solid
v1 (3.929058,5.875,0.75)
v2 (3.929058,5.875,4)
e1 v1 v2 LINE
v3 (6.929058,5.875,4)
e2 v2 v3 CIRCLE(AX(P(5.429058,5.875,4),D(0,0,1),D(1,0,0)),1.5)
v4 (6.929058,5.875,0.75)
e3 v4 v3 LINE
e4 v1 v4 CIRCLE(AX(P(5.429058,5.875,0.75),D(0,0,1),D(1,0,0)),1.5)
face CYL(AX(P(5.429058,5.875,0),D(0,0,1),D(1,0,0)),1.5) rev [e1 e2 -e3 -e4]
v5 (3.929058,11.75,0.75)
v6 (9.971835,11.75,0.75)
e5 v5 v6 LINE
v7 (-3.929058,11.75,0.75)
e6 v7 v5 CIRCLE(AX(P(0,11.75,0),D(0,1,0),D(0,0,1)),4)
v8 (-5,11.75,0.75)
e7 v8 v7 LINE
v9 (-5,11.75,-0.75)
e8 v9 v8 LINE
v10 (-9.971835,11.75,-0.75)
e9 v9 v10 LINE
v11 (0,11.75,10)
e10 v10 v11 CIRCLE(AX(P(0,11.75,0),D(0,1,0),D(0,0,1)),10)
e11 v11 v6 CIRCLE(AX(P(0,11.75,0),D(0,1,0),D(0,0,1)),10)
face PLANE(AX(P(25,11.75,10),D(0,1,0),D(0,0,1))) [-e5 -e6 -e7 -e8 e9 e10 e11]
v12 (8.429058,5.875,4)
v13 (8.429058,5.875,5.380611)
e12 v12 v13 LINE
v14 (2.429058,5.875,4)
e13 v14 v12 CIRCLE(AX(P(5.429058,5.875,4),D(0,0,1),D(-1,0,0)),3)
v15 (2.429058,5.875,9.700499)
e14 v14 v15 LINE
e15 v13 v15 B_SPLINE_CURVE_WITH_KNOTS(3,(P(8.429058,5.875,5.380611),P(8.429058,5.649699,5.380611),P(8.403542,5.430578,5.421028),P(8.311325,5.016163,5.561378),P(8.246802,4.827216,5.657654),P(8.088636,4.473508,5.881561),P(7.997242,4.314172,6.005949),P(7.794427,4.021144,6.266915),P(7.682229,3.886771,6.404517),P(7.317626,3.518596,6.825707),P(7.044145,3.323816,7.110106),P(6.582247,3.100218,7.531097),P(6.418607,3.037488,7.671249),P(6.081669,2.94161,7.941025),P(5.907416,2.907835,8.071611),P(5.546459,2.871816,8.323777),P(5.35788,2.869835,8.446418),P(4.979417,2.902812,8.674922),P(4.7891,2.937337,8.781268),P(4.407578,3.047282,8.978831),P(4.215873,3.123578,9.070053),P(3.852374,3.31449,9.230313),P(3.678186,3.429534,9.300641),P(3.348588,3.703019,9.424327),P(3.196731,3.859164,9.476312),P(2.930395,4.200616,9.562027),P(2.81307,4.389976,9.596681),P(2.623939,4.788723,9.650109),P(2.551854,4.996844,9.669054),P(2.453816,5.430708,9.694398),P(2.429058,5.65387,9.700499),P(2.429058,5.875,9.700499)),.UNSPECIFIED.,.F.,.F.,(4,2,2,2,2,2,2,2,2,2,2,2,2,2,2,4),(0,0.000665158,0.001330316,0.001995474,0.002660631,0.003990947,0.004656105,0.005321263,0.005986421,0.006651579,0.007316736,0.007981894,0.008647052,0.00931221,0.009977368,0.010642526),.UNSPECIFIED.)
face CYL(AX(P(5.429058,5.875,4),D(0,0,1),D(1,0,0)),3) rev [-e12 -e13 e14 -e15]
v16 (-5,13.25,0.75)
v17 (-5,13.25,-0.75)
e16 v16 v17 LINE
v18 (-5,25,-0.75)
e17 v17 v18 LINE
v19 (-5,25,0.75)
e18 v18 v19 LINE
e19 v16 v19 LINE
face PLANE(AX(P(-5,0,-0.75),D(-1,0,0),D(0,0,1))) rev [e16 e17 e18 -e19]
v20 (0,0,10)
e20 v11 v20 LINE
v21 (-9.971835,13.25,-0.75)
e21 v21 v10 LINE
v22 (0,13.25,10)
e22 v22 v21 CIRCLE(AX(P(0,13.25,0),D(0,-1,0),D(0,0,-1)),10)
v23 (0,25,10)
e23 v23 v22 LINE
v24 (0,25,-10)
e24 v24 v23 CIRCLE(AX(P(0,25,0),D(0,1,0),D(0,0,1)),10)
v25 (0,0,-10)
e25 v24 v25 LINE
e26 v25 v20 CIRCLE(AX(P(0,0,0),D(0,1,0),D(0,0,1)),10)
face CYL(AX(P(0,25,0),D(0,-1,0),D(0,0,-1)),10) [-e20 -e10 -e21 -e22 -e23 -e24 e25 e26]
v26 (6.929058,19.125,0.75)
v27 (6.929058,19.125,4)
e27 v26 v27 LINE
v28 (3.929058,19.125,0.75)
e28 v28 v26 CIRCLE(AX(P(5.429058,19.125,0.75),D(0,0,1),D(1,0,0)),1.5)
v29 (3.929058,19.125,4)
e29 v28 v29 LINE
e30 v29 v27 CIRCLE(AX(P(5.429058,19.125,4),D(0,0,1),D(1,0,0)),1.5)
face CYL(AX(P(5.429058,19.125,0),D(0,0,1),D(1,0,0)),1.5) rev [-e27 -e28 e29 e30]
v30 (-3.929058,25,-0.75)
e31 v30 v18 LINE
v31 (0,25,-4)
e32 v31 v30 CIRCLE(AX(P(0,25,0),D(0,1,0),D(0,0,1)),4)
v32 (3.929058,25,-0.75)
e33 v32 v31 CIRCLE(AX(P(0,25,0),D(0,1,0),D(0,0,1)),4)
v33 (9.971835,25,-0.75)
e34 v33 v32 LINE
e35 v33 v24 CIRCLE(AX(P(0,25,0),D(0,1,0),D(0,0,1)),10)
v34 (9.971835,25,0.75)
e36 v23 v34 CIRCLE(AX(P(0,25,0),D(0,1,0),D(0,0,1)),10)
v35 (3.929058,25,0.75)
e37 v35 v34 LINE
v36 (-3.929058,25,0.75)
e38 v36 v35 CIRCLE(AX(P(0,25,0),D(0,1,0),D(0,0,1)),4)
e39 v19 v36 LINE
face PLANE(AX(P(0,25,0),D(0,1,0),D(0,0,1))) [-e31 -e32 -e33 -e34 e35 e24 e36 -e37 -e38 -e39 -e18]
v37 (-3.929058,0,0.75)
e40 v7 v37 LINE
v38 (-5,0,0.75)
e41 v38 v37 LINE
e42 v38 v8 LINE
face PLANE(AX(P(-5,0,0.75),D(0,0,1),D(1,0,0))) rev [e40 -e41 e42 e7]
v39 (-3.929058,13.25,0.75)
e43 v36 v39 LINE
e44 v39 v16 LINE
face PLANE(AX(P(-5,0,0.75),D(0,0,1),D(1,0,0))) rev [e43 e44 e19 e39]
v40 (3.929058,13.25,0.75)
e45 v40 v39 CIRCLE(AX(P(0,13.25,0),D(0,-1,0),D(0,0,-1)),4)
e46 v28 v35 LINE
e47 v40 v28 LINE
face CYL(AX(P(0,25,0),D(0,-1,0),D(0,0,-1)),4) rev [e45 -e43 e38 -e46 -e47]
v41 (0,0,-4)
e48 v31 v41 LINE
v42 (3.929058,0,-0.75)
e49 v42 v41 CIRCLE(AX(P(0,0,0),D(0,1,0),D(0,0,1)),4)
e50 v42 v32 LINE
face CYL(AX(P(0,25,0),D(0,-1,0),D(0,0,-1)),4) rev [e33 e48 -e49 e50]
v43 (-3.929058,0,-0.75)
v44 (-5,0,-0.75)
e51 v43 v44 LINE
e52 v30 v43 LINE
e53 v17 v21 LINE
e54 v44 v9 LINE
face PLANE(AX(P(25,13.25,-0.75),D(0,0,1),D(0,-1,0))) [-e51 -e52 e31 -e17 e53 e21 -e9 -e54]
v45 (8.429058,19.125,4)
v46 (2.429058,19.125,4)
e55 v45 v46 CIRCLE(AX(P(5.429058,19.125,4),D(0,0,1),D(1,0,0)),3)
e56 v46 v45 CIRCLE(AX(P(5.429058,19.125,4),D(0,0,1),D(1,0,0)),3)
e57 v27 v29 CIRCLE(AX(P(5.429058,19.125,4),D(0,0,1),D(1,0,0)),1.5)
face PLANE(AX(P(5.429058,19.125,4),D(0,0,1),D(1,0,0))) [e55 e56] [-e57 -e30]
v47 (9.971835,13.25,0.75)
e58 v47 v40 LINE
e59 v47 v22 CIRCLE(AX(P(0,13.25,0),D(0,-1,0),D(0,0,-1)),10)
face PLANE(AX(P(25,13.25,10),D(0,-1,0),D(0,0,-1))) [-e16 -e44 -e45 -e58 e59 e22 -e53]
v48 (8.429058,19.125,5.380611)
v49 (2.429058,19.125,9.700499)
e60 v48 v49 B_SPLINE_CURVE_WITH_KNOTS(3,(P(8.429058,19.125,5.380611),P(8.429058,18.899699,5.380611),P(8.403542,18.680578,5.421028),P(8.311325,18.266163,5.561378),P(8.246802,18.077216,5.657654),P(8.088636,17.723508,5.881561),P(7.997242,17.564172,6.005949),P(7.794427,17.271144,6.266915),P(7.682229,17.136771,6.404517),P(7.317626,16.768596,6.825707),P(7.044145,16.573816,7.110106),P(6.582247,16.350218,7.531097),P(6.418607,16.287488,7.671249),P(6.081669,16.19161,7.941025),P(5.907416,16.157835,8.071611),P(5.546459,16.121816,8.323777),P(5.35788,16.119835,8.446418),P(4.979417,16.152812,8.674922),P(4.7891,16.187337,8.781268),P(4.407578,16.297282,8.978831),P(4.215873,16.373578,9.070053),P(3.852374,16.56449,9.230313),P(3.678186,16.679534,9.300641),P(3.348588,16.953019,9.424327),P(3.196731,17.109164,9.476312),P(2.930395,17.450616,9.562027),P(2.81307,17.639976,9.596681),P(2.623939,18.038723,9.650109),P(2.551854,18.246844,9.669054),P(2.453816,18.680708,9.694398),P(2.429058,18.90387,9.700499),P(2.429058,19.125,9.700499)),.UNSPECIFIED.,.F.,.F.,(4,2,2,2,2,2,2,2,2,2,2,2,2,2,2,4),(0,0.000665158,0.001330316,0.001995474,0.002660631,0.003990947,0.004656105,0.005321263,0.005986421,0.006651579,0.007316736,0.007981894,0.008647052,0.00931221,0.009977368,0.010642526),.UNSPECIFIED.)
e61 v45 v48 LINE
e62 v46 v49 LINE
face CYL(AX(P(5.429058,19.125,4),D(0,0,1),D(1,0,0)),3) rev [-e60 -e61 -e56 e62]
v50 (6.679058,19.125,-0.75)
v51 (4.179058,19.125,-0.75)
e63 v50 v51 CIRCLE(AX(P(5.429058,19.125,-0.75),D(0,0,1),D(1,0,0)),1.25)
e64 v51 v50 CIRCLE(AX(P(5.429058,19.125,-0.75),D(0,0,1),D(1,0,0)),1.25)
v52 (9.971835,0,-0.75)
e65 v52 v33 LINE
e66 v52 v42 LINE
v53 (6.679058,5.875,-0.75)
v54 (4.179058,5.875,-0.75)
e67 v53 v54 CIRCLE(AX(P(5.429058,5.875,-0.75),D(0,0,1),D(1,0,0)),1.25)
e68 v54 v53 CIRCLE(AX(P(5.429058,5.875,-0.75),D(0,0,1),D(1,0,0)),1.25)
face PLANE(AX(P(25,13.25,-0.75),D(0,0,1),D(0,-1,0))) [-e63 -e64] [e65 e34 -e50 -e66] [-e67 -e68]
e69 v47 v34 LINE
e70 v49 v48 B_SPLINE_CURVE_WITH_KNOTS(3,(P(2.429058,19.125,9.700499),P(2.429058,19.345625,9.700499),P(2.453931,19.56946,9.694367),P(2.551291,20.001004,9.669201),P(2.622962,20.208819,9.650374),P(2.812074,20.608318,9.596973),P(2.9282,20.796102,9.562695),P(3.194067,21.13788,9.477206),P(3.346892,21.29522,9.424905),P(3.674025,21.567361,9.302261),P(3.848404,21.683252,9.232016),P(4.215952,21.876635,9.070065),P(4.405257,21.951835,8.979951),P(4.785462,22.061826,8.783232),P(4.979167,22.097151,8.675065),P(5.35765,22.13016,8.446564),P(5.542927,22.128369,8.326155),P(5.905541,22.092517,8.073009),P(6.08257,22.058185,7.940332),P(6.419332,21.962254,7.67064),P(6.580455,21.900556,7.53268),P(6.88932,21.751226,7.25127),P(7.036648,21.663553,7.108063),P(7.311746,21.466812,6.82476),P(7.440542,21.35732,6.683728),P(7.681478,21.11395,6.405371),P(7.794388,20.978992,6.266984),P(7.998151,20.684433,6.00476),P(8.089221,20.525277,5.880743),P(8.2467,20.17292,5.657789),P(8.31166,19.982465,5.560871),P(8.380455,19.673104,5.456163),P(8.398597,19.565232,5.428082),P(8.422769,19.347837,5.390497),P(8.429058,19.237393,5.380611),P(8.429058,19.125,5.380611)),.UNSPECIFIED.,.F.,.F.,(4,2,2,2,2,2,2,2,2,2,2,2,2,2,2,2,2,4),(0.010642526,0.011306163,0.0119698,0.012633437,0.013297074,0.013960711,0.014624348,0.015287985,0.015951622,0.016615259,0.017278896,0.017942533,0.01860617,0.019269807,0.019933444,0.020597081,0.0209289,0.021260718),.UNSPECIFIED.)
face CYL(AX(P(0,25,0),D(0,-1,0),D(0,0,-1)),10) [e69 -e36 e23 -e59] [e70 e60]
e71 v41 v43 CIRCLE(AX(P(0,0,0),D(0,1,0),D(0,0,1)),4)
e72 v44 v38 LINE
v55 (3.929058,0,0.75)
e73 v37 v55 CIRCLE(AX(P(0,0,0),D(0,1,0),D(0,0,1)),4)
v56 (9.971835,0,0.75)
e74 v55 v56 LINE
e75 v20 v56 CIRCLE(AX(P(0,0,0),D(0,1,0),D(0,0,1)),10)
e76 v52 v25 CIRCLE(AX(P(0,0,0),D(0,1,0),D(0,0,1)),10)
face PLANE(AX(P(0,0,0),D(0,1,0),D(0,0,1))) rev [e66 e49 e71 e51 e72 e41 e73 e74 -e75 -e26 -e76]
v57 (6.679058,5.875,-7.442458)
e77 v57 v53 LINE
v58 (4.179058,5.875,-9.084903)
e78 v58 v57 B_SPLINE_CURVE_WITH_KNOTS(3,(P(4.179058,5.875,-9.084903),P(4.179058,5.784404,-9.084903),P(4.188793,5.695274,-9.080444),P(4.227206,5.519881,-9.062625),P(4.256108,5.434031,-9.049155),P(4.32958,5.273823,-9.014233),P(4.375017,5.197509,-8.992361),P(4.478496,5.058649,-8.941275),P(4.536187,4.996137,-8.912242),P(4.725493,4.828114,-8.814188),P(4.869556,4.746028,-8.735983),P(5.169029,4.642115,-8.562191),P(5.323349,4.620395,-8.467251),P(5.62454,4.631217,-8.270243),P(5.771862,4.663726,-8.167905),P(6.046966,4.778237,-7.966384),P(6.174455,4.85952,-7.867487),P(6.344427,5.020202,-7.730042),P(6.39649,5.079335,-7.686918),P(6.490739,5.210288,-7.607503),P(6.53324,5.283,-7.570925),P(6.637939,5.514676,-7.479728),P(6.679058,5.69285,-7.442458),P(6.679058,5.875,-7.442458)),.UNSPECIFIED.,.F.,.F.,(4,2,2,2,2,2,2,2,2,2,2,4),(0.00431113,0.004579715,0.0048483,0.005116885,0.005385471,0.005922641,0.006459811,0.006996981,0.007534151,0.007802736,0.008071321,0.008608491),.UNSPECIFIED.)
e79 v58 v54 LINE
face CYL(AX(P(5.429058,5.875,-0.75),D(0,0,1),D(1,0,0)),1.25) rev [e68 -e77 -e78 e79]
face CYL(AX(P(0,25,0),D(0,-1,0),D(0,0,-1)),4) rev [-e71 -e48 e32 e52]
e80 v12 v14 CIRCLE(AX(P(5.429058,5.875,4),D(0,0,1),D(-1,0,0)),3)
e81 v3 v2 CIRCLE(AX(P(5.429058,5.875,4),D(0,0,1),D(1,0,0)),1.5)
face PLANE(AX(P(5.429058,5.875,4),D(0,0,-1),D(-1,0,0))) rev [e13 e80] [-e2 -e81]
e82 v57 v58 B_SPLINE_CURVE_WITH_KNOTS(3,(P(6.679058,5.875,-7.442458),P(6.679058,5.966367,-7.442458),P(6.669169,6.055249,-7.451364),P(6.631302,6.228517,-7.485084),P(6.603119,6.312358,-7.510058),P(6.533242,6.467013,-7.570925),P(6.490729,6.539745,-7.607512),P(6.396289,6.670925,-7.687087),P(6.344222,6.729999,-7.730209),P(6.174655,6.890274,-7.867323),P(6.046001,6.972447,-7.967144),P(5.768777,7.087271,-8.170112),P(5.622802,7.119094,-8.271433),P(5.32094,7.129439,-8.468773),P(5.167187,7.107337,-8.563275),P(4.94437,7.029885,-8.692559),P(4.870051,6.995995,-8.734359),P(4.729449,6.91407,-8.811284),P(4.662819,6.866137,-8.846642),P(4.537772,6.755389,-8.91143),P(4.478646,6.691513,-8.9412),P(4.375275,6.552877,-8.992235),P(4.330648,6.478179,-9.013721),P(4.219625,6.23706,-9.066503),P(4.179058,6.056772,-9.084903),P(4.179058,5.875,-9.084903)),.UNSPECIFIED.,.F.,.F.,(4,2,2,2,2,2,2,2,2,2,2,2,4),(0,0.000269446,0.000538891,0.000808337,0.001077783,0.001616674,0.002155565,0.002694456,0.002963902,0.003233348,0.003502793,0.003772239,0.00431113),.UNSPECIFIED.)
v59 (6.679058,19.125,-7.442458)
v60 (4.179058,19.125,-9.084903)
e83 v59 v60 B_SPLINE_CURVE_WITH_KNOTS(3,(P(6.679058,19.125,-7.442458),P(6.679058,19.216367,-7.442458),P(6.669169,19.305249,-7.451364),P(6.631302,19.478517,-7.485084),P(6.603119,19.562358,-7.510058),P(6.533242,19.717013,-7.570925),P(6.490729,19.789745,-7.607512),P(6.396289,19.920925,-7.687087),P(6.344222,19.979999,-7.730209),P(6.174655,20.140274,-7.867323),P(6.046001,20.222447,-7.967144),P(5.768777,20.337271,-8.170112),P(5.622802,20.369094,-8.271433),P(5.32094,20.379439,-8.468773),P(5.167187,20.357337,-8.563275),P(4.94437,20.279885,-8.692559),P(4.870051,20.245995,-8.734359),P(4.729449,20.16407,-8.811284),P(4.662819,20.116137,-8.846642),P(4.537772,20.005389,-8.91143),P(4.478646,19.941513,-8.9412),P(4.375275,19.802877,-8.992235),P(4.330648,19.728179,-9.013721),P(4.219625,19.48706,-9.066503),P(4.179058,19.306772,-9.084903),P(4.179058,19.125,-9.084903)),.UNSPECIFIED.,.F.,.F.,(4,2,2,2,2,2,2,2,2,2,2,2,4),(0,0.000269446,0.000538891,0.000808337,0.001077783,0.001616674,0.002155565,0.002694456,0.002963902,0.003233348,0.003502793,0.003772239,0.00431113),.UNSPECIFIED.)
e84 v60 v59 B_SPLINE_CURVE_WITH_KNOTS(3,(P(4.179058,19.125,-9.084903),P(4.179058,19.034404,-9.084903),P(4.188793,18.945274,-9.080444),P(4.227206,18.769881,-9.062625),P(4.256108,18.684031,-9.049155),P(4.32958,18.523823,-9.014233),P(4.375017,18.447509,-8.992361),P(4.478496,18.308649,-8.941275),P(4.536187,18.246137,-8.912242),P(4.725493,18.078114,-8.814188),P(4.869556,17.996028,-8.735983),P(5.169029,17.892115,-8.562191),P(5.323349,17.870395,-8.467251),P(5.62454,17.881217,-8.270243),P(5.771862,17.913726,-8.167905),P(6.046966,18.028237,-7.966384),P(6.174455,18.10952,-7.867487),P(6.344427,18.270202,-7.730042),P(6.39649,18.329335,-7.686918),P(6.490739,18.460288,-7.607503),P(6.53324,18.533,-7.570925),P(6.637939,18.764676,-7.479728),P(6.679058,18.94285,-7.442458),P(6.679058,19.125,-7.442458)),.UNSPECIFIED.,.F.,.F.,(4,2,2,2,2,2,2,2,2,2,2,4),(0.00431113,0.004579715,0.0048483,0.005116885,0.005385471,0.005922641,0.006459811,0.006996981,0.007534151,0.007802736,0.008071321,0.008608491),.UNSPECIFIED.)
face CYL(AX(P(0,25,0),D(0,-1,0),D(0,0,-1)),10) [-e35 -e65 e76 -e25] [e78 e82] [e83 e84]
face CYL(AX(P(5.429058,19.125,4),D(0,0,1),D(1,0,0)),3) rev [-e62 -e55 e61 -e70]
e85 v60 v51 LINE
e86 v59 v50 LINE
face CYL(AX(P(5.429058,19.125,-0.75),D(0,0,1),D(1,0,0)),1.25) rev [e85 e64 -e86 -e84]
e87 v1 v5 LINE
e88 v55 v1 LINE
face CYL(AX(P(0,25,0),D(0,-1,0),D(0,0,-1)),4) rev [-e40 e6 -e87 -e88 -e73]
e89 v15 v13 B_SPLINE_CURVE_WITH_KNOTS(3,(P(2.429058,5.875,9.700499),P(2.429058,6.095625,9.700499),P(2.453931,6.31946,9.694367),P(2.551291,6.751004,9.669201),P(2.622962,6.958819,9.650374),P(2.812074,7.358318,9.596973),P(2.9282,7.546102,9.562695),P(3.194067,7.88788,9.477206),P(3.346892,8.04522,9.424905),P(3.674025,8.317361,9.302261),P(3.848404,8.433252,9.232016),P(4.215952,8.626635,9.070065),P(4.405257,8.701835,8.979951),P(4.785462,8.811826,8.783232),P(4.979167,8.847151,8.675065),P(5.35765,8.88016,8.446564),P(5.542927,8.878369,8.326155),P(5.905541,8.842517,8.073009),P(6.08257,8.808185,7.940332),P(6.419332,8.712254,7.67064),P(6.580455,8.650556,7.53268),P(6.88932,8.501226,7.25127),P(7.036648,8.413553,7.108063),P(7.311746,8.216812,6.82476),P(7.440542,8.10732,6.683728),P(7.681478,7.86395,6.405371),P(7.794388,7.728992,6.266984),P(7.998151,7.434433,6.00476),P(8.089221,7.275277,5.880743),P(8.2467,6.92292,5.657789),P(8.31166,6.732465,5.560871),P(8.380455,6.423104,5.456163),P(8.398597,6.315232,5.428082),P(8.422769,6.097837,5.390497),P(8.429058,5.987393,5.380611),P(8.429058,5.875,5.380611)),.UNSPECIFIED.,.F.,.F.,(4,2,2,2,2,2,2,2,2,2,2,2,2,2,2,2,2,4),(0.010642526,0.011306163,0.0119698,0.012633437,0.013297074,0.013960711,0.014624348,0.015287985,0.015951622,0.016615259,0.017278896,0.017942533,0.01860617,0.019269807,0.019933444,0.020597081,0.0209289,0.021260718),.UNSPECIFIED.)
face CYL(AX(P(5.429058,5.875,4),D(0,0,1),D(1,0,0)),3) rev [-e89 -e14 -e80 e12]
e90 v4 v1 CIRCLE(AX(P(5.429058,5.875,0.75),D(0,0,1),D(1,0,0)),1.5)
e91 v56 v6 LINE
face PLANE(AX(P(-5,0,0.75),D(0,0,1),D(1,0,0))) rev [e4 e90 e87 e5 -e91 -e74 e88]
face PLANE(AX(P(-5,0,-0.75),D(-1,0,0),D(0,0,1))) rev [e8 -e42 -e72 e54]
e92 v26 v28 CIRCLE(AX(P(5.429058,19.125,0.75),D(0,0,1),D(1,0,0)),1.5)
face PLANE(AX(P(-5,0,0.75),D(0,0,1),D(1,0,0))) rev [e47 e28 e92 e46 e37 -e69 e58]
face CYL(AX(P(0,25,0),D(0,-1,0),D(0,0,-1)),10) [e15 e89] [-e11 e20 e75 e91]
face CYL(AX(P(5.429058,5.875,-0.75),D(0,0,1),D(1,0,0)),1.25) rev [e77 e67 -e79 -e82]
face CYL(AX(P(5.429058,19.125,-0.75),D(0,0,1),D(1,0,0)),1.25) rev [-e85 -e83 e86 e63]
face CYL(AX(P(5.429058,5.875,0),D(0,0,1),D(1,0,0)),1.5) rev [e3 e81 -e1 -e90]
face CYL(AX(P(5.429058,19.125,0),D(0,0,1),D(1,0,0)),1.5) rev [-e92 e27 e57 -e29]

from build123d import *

# Parameters (mm, degrees)
SKETCH2_R               = 10
SKETCH2_R_2             = 4
BOSS_EXTRUDE1_DEPTH     = 25
CUT_EXTRUDE1_DEPTH      = 25
CUT_EXTRUDE1_DEPTH_BACK = 25
SKETCH3_W               = 10.75
SKETCH3_H               = 1.5
SKETCH4_W               = 17.874578158
SKETCH4_H               = 1.5
CUT_EXTRUDE2_DEPTH      = 29.722813233
SKETCH5_R               = 3
CUT_EXTRUDE3_DEPTH      = 6
SKETCH6_R               = 1.5
CUT_EXTRUDE4_DEPTH      = 4
M3_TAPPED_HOLE3_D       = 2.5


with BuildPart() as part:
    # Sketch2 → Boss-Extrude1 (new body)
    with BuildSketch(Plane(origin=(0, 0, 0), x_dir=(1, 0, 0), z_dir=(0, 1, 0))):
        with Locations(Location((0, 0, 0), (0, 0, 270))):
            Circle(SKETCH2_R)
        with Locations(Location((0, 0, 0), (0, 0, 270))):
            Circle(SKETCH2_R_2, mode=Mode.SUBTRACT)
    extrude(amount=BOSS_EXTRUDE1_DEPTH)

    # Sketch3 → Cut-Extrude1 (cut, two sides: drawn at the far end of the back side and taken through both)
    with BuildSketch(Plane(origin=(0, 0, 0), x_dir=(0, 0, -1), z_dir=(1, 0, 0)).offset(-CUT_EXTRUDE1_DEPTH_BACK)):
        with Locations((-4.625, 12.5)):
            Rectangle(SKETCH3_W, SKETCH3_H)
    extrude(amount=CUT_EXTRUDE1_DEPTH + CUT_EXTRUDE1_DEPTH_BACK, mode=Mode.SUBTRACT)

    # Sketch4 → Cut-Extrude2 (cut, through all)
    with BuildSketch(Plane(origin=(0, 25, 0), x_dir=(1, 0, 0), z_dir=(0, 1, 0))):
        with Locations((3.937289079, 0)):
            Rectangle(SKETCH4_W, SKETCH4_H)
    extrude(amount=-CUT_EXTRUDE2_DEPTH, mode=Mode.SUBTRACT)

    # Sketch5 → Cut-Extrude3 (cut)
    with BuildSketch(Plane.XY.offset(10)):
        with Locations((5.429058411, 19.125)):
            Circle(SKETCH5_R)
        with Locations((5.429058411, 5.875)):
            Circle(SKETCH5_R)
    extrude(amount=-CUT_EXTRUDE3_DEPTH, mode=Mode.SUBTRACT)

    # Sketch6 → Cut-Extrude4 (cut)
    with BuildSketch(Plane.XY.offset(4)):
        with Locations((5.429058411, 5.875)):
            Circle(SKETCH6_R)
        with Locations((5.429058411, 19.125)):
            Circle(SKETCH6_R)
    extrude(amount=-CUT_EXTRUDE4_DEPTH, mode=Mode.SUBTRACT)

    # M3 Tapped Hole3 (through all)
    with Locations(Plane.XY.offset(-0.75)):
        with Locations((5.429058411, 19.125), (5.429058411, 5.875)):
            Hole(M3_TAPPED_HOLE3_D / 2)


solid = part.part
